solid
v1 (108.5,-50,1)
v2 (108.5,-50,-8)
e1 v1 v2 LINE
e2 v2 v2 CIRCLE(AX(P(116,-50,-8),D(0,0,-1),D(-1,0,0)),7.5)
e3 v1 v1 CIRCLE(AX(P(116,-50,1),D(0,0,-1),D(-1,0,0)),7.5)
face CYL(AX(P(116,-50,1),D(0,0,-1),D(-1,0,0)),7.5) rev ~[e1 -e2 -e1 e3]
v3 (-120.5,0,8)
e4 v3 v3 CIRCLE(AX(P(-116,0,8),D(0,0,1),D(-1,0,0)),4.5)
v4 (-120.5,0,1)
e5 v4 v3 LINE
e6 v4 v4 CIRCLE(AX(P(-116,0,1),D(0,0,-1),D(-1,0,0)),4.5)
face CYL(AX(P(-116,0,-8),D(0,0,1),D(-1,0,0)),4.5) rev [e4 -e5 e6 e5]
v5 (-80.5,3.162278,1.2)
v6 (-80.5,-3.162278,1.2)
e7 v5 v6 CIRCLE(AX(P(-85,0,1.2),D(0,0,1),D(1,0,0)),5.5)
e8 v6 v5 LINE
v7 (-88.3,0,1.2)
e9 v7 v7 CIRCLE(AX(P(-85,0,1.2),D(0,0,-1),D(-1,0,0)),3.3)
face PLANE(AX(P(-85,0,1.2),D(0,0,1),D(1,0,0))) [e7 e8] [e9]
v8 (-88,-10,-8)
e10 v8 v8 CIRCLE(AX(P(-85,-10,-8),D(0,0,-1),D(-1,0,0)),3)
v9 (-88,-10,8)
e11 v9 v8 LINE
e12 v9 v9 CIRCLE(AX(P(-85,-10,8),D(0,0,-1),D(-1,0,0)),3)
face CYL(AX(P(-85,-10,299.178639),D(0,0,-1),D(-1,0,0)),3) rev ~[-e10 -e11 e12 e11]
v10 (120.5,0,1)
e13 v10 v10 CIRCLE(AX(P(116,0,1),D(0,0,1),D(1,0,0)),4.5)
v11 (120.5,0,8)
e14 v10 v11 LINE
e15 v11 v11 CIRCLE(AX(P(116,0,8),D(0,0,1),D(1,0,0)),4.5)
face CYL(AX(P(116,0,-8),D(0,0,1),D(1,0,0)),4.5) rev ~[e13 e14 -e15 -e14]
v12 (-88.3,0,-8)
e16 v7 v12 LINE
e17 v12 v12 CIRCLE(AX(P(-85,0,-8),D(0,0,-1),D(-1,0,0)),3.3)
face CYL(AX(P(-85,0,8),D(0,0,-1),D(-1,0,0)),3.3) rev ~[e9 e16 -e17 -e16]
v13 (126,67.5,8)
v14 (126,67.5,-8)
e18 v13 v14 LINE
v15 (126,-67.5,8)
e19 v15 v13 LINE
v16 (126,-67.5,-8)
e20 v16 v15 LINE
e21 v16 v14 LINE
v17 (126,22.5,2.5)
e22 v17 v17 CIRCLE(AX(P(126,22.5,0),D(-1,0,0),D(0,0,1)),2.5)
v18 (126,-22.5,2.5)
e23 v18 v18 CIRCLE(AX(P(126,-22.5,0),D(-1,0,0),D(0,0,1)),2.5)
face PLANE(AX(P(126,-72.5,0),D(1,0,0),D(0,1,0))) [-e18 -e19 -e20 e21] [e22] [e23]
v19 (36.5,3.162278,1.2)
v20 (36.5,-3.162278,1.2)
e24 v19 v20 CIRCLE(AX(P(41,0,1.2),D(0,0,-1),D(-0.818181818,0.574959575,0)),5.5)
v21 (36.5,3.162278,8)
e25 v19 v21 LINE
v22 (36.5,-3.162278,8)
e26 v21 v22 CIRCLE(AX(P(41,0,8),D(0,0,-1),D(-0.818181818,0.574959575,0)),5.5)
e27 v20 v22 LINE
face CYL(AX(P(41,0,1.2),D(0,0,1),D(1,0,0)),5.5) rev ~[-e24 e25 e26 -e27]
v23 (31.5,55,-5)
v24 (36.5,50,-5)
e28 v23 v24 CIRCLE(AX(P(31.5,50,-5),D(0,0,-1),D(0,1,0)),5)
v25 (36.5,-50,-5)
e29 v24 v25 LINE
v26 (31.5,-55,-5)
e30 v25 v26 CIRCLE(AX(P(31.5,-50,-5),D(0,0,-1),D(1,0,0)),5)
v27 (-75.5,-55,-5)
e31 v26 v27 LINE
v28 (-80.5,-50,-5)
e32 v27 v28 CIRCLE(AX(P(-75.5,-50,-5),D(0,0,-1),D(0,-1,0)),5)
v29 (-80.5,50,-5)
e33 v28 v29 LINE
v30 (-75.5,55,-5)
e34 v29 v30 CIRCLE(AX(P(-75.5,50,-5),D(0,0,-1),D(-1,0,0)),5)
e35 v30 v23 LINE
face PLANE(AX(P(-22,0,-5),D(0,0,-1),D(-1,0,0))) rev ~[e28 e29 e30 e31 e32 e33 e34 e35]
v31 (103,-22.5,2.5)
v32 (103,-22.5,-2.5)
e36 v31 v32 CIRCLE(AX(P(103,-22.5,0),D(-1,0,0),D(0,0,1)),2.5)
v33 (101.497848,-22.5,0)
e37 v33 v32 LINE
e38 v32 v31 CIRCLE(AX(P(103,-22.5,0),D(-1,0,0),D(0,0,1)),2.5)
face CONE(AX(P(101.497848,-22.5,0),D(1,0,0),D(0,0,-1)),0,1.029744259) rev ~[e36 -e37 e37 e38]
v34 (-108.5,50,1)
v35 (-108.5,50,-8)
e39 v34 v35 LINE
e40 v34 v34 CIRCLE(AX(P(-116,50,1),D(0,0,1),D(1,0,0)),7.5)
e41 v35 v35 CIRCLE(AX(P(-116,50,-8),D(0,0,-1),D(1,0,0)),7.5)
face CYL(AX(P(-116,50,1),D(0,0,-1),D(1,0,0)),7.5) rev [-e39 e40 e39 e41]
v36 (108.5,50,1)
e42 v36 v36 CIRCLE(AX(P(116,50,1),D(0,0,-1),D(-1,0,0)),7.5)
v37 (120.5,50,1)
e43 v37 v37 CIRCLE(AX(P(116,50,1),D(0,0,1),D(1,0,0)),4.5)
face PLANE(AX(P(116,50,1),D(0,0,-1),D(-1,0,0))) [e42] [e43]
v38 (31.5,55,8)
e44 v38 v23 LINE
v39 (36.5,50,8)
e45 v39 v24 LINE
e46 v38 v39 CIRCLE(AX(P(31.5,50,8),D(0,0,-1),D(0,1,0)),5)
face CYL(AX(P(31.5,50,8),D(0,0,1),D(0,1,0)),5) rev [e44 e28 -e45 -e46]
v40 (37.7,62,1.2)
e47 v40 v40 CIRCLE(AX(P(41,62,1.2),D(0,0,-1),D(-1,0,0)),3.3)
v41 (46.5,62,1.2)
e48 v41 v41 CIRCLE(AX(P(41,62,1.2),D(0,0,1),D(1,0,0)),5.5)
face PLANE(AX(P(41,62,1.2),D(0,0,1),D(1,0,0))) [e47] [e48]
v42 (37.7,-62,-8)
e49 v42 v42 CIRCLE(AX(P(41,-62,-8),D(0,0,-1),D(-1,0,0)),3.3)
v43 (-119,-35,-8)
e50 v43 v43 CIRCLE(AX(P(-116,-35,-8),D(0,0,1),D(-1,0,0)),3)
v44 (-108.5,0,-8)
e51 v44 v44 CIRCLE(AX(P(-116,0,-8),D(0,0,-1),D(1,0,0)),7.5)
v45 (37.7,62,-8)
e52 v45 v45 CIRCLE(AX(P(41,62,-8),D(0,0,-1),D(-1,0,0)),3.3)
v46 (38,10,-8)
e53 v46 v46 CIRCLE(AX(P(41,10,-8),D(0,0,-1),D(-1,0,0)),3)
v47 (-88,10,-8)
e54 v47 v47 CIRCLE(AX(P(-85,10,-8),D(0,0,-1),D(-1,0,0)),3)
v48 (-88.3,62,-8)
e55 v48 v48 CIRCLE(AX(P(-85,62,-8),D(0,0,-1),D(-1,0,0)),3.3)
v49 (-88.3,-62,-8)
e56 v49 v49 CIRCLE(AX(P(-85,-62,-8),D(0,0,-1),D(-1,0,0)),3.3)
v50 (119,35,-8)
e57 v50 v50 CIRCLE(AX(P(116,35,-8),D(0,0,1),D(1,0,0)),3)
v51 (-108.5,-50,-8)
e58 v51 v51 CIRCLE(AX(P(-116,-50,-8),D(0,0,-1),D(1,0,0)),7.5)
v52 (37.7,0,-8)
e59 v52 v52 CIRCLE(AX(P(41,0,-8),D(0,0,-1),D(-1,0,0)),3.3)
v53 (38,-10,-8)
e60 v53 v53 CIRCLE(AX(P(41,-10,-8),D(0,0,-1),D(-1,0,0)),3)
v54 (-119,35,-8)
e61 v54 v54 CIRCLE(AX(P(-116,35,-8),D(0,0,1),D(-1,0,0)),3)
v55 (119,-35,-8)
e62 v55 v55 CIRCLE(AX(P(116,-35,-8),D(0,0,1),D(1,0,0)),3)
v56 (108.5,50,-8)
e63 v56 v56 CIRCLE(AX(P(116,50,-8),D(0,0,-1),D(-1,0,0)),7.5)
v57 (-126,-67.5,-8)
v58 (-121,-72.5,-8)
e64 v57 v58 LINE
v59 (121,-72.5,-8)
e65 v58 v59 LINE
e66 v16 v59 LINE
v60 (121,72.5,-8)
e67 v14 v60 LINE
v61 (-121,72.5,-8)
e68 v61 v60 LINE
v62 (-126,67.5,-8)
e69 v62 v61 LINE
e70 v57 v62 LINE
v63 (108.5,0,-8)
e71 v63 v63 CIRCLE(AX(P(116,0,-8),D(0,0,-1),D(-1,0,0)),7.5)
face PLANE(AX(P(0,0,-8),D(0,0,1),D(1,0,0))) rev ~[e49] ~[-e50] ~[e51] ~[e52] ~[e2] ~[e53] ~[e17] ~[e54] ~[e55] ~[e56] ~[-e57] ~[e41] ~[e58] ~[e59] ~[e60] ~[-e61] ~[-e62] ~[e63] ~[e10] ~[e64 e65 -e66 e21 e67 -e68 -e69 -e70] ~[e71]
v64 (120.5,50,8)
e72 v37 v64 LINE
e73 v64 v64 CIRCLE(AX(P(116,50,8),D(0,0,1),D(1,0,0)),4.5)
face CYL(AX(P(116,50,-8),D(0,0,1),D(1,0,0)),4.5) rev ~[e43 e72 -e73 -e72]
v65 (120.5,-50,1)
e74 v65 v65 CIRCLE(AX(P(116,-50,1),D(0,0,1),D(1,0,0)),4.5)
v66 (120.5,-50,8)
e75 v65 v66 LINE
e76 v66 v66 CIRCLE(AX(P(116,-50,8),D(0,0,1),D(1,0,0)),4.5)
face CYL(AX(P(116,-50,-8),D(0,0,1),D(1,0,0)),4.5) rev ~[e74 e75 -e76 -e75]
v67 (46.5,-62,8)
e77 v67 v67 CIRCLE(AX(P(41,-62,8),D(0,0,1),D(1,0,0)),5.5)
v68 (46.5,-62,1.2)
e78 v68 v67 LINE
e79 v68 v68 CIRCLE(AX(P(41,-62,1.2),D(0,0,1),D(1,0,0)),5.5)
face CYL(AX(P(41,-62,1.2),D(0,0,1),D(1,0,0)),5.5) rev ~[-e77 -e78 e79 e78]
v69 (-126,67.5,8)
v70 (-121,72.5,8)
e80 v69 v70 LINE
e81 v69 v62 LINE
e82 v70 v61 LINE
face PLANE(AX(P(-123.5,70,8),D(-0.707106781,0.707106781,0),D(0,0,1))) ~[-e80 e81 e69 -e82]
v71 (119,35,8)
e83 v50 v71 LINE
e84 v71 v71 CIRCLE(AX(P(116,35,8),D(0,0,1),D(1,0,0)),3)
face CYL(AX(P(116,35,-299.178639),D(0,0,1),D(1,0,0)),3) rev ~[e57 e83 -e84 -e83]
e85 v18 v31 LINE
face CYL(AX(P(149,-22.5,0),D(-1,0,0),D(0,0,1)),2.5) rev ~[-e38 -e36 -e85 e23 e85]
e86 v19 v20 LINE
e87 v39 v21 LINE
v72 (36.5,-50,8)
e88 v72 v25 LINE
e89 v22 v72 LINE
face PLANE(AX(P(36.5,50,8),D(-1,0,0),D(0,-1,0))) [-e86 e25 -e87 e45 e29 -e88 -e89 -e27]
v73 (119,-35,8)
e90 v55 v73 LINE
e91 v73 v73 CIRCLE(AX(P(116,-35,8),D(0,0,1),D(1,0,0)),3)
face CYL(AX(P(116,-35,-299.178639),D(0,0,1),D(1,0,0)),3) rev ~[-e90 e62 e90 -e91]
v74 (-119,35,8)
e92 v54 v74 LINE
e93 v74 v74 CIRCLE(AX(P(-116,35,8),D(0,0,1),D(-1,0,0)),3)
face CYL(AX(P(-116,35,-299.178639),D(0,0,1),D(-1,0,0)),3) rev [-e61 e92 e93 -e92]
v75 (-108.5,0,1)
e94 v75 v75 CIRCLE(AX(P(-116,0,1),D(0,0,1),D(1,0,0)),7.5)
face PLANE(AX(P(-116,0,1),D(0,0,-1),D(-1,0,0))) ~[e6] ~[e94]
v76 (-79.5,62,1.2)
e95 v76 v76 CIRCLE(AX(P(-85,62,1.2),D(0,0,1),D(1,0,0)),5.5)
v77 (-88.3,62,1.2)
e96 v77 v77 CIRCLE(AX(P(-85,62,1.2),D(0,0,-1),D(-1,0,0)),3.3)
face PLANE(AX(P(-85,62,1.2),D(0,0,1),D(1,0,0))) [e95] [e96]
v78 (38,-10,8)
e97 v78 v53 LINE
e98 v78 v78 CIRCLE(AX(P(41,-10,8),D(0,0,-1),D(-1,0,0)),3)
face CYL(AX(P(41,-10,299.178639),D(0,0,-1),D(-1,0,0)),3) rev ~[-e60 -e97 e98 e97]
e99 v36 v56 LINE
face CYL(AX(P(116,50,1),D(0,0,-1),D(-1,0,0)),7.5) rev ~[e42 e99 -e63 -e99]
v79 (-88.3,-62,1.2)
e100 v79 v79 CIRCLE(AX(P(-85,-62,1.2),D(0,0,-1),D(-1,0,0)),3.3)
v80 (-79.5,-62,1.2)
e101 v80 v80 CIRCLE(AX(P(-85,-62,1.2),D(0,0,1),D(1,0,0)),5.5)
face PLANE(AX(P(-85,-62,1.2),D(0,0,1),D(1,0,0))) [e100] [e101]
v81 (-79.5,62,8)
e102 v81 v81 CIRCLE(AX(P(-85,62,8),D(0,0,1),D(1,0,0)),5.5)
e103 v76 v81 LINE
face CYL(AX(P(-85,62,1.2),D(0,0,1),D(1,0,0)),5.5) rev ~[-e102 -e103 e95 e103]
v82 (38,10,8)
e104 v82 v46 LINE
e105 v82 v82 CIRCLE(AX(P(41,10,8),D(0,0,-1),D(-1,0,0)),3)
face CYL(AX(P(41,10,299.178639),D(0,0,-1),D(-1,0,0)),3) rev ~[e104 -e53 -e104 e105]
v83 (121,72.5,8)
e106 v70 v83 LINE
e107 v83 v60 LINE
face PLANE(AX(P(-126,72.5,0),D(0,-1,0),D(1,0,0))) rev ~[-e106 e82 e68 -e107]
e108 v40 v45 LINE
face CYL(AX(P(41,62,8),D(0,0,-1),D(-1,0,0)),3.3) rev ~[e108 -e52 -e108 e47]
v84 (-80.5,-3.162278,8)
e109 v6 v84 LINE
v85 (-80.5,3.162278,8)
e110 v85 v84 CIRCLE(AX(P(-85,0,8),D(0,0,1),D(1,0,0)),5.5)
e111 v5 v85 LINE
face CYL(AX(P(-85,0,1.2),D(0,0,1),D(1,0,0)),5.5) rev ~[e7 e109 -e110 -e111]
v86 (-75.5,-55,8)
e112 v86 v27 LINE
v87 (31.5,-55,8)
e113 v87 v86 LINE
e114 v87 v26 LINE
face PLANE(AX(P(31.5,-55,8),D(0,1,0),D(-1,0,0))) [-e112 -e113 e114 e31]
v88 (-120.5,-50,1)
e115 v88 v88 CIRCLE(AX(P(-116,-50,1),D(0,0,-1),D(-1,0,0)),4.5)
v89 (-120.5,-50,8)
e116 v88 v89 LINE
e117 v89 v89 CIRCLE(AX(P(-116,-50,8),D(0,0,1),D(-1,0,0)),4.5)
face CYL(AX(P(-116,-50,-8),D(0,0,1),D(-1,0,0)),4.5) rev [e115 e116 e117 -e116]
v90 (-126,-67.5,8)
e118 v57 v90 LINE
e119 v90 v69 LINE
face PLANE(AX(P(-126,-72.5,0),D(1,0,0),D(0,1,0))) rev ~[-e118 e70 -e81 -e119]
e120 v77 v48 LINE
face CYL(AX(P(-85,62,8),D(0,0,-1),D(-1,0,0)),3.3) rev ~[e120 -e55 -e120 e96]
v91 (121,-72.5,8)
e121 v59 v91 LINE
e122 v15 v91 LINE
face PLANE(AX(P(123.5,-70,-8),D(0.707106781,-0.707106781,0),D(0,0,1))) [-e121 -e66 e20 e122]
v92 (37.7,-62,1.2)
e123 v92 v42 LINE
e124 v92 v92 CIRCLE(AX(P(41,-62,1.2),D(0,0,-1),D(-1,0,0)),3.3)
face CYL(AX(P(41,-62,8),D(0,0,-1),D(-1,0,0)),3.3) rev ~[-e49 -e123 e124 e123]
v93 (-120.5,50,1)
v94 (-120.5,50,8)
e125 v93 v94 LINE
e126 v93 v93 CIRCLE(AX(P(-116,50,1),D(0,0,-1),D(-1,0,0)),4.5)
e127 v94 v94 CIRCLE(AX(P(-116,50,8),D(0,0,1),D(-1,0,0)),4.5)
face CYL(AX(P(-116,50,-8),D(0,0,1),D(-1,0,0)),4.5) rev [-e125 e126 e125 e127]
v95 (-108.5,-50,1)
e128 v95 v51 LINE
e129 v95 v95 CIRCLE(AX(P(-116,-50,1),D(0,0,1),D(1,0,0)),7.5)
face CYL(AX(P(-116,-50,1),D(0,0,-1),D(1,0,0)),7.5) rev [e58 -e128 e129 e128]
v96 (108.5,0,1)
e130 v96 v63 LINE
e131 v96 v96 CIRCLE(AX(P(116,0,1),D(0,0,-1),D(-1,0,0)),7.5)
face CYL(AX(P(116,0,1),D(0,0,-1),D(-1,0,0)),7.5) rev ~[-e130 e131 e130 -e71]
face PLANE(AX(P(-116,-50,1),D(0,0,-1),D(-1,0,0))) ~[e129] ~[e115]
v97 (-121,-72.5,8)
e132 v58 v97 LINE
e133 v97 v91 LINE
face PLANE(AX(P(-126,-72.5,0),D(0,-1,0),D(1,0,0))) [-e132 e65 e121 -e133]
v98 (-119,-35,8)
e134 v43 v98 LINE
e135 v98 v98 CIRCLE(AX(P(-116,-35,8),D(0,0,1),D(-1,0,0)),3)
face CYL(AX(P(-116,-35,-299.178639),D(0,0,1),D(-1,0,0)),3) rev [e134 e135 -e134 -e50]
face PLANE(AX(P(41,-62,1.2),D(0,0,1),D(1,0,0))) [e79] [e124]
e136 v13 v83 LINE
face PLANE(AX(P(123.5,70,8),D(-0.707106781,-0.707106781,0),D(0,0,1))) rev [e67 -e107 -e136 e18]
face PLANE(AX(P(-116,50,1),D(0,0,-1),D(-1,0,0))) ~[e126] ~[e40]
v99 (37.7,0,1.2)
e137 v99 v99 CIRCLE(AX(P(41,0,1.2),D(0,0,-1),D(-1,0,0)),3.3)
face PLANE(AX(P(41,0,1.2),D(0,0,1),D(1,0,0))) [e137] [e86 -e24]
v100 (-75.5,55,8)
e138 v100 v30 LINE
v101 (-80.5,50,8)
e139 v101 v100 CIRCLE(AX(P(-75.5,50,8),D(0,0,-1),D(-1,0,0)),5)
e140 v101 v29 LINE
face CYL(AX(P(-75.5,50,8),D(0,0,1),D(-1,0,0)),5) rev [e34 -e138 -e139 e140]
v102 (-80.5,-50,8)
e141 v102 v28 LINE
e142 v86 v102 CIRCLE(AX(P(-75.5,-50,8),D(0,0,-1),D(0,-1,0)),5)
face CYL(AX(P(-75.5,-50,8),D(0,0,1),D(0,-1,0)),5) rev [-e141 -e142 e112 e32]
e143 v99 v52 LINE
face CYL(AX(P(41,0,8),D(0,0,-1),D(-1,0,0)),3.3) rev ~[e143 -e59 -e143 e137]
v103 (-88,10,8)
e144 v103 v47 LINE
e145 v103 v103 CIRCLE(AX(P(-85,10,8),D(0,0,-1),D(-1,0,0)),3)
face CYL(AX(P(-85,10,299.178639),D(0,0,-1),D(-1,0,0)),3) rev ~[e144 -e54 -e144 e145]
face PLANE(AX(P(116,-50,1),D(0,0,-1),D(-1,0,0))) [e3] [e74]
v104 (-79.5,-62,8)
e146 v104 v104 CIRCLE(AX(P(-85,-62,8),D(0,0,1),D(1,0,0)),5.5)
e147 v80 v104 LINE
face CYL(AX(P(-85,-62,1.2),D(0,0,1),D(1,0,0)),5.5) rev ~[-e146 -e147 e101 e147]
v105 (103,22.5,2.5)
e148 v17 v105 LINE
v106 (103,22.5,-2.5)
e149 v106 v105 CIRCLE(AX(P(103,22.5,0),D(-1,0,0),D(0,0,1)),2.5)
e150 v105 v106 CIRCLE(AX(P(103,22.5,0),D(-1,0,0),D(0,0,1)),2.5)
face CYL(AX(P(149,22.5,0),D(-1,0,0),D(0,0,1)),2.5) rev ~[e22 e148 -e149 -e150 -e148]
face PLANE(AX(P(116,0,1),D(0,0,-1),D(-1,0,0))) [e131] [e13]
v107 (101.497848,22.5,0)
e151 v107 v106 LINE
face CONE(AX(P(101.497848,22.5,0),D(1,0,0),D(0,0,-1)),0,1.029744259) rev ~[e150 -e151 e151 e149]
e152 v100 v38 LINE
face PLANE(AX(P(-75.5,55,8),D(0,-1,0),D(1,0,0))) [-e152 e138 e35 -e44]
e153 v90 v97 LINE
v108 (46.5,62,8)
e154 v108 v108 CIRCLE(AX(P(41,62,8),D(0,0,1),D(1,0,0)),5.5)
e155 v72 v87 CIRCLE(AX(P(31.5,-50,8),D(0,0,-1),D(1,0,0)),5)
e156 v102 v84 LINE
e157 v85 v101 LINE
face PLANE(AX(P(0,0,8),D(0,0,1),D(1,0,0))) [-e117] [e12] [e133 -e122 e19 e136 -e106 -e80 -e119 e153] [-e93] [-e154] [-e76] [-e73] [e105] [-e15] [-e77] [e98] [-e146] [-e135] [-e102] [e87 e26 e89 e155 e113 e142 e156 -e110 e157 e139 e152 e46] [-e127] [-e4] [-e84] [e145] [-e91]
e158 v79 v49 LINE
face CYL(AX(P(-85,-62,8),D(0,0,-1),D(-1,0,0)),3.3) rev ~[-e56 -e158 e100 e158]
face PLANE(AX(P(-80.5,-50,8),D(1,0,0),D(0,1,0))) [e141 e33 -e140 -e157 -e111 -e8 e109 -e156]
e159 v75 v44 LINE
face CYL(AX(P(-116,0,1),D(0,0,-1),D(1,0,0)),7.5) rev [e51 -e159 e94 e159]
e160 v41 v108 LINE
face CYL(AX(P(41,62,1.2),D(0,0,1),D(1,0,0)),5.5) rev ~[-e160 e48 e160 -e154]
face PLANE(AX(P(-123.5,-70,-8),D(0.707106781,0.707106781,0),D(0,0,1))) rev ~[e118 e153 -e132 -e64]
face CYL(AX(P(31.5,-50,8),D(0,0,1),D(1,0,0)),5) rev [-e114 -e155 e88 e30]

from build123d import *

# Parameters (mm, degrees)
SKETCH_1_W                  = 252
SKETCH_1_H                  = 145
EXTRUDE_1_DEPTH             = 8
HOLE_WIZARD_2_D             = 6.6
HOLE_WIZARD_2_CBORE_D       = 11
HOLE_WIZARD_2_CBORE_DEPTH   = 6.8
HOLE_WIZARD_2_2_D           = 9
HOLE_WIZARD_2_2_CBORE_D     = 15
HOLE_WIZARD_2_2_CBORE_DEPTH = 9
HOLE_WIZARD_6_0_6_1_D       = 6
HOLE_WIZARD_6_0_6_2_D       = 6
CUT_EXTRUDE_1_DEPTH         = 13
CHAMFER_1_SIZE              = 5
HOLE_WIZARD_M6_2_D          = 5
HOLE_WIZARD_M6_2_DEPTH      = 23
HOLE_WIZARD_M6_2_TIP        = 1.502151548


with BuildPart() as part:
    # 草图1 → 凸台-拉伸1 (new, symmetric)
    with BuildSketch(Plane.XY):
        Rectangle(SKETCH_1_W, SKETCH_1_H)
    extrude(amount=EXTRUDE_1_DEPTH, both=True)

    # Hole Wizard 2 (through all)
    with Locations(Plane.XY.offset(8)):
        with Locations((-85, 62), (-85, 0), (41, 62), (41, 0), (41, -62), (-85, -62)):
            CounterBoreHole(HOLE_WIZARD_2_D / 2, HOLE_WIZARD_2_CBORE_D / 2, HOLE_WIZARD_2_CBORE_DEPTH)

    # Hole Wizard 2 2 (through all)
    with Locations(Plane(origin=(0, 0, -8), x_dir=(-1, 0, 0), z_dir=(0, 0, -1))):
        with Locations((-116, -50), (-116, 0), (-116, 50)):
            hole_wizard_2_2 = CounterBoreHole(HOLE_WIZARD_2_2_D / 2, HOLE_WIZARD_2_2_CBORE_D / 2, HOLE_WIZARD_2_2_CBORE_DEPTH)

    # Ø6.0 (6) 直径孔1 (through all)
    with Locations(Plane(origin=(0, 0, -8), x_dir=(-1, 0, 0), z_dir=(0, 0, -1))):
        with Locations((-116, -35), (-116, 35)):
            hole_wizard_6_0_6_1 = Hole(HOLE_WIZARD_6_0_6_1_D / 2)

    # 镜向1: Hole Wizard 2 2, Ø6.0 (6) 直径孔1 across plane
    add(hole_wizard_2_2.mirror(Plane(origin=(0, 0, 0), x_dir=(0, 0, 1), z_dir=(1, 0, 0))), mode=Mode.SUBTRACT)
    add(hole_wizard_6_0_6_1.mirror(Plane(origin=(0, 0, 0), x_dir=(0, 0, 1), z_dir=(1, 0, 0))), mode=Mode.SUBTRACT)

    # Ø6.0 (6) 直径孔2 (through all)
    with Locations(Plane.XY.offset(8)):
        with Locations((41, -10), (-85, -10), (-85, 10), (41, 10)):
            Hole(HOLE_WIZARD_6_0_6_2_D / 2)

    # 草图10 → 切除-拉伸1 (cut)
    with BuildSketch(Plane.XY.offset(8)):
        with BuildLine():
            Line((-75.5, 55), (31.5, 55))
            ThreePointArc((31.5, 55), (35.035533906, 53.535533906), (36.5, 50))
            Line((36.5, 50), (36.5, -50))
            ThreePointArc((36.5, -50), (35.035533906, -53.535533906), (31.5, -55))
            Line((31.5, -55), (-75.5, -55))
            ThreePointArc((-75.5, -55), (-79.035533906, -53.535533906), (-80.5, -50))
            Line((-80.5, -50), (-80.5, 50))
            ThreePointArc((-80.5, 50), (-79.035533906, 53.535533906), (-75.5, 55))
        make_face()
    extrude(amount=-CUT_EXTRUDE_1_DEPTH, mode=Mode.SUBTRACT)

    # 倒角1
    chamfer_1_edges = [part.edges().sort_by_distance(p)[0] for p in [
        (-126, 72.5, 0),
        (126, 72.5, 0),
        (126, -72.5, 0),
        (-126, -72.5, 0),
    ]]
    chamfer(chamfer_1_edges, length=CHAMFER_1_SIZE)

    # M6 螺纹孔2
    with Locations(Plane(origin=(126, 0, 0), x_dir=(0, 0, -1), z_dir=(1, 0, 0))):
        with Locations((0, 22.5), (0, -22.5)):
            Hole(HOLE_WIZARD_M6_2_D / 2, depth=HOLE_WIZARD_M6_2_DEPTH)
            with Locations((0, 0, -(HOLE_WIZARD_M6_2_DEPTH + HOLE_WIZARD_M6_2_TIP / 2))):  # 118° drill point
                Cone(0, HOLE_WIZARD_M6_2_D / 2, HOLE_WIZARD_M6_2_TIP, mode=Mode.SUBTRACT)


solid = part.part
